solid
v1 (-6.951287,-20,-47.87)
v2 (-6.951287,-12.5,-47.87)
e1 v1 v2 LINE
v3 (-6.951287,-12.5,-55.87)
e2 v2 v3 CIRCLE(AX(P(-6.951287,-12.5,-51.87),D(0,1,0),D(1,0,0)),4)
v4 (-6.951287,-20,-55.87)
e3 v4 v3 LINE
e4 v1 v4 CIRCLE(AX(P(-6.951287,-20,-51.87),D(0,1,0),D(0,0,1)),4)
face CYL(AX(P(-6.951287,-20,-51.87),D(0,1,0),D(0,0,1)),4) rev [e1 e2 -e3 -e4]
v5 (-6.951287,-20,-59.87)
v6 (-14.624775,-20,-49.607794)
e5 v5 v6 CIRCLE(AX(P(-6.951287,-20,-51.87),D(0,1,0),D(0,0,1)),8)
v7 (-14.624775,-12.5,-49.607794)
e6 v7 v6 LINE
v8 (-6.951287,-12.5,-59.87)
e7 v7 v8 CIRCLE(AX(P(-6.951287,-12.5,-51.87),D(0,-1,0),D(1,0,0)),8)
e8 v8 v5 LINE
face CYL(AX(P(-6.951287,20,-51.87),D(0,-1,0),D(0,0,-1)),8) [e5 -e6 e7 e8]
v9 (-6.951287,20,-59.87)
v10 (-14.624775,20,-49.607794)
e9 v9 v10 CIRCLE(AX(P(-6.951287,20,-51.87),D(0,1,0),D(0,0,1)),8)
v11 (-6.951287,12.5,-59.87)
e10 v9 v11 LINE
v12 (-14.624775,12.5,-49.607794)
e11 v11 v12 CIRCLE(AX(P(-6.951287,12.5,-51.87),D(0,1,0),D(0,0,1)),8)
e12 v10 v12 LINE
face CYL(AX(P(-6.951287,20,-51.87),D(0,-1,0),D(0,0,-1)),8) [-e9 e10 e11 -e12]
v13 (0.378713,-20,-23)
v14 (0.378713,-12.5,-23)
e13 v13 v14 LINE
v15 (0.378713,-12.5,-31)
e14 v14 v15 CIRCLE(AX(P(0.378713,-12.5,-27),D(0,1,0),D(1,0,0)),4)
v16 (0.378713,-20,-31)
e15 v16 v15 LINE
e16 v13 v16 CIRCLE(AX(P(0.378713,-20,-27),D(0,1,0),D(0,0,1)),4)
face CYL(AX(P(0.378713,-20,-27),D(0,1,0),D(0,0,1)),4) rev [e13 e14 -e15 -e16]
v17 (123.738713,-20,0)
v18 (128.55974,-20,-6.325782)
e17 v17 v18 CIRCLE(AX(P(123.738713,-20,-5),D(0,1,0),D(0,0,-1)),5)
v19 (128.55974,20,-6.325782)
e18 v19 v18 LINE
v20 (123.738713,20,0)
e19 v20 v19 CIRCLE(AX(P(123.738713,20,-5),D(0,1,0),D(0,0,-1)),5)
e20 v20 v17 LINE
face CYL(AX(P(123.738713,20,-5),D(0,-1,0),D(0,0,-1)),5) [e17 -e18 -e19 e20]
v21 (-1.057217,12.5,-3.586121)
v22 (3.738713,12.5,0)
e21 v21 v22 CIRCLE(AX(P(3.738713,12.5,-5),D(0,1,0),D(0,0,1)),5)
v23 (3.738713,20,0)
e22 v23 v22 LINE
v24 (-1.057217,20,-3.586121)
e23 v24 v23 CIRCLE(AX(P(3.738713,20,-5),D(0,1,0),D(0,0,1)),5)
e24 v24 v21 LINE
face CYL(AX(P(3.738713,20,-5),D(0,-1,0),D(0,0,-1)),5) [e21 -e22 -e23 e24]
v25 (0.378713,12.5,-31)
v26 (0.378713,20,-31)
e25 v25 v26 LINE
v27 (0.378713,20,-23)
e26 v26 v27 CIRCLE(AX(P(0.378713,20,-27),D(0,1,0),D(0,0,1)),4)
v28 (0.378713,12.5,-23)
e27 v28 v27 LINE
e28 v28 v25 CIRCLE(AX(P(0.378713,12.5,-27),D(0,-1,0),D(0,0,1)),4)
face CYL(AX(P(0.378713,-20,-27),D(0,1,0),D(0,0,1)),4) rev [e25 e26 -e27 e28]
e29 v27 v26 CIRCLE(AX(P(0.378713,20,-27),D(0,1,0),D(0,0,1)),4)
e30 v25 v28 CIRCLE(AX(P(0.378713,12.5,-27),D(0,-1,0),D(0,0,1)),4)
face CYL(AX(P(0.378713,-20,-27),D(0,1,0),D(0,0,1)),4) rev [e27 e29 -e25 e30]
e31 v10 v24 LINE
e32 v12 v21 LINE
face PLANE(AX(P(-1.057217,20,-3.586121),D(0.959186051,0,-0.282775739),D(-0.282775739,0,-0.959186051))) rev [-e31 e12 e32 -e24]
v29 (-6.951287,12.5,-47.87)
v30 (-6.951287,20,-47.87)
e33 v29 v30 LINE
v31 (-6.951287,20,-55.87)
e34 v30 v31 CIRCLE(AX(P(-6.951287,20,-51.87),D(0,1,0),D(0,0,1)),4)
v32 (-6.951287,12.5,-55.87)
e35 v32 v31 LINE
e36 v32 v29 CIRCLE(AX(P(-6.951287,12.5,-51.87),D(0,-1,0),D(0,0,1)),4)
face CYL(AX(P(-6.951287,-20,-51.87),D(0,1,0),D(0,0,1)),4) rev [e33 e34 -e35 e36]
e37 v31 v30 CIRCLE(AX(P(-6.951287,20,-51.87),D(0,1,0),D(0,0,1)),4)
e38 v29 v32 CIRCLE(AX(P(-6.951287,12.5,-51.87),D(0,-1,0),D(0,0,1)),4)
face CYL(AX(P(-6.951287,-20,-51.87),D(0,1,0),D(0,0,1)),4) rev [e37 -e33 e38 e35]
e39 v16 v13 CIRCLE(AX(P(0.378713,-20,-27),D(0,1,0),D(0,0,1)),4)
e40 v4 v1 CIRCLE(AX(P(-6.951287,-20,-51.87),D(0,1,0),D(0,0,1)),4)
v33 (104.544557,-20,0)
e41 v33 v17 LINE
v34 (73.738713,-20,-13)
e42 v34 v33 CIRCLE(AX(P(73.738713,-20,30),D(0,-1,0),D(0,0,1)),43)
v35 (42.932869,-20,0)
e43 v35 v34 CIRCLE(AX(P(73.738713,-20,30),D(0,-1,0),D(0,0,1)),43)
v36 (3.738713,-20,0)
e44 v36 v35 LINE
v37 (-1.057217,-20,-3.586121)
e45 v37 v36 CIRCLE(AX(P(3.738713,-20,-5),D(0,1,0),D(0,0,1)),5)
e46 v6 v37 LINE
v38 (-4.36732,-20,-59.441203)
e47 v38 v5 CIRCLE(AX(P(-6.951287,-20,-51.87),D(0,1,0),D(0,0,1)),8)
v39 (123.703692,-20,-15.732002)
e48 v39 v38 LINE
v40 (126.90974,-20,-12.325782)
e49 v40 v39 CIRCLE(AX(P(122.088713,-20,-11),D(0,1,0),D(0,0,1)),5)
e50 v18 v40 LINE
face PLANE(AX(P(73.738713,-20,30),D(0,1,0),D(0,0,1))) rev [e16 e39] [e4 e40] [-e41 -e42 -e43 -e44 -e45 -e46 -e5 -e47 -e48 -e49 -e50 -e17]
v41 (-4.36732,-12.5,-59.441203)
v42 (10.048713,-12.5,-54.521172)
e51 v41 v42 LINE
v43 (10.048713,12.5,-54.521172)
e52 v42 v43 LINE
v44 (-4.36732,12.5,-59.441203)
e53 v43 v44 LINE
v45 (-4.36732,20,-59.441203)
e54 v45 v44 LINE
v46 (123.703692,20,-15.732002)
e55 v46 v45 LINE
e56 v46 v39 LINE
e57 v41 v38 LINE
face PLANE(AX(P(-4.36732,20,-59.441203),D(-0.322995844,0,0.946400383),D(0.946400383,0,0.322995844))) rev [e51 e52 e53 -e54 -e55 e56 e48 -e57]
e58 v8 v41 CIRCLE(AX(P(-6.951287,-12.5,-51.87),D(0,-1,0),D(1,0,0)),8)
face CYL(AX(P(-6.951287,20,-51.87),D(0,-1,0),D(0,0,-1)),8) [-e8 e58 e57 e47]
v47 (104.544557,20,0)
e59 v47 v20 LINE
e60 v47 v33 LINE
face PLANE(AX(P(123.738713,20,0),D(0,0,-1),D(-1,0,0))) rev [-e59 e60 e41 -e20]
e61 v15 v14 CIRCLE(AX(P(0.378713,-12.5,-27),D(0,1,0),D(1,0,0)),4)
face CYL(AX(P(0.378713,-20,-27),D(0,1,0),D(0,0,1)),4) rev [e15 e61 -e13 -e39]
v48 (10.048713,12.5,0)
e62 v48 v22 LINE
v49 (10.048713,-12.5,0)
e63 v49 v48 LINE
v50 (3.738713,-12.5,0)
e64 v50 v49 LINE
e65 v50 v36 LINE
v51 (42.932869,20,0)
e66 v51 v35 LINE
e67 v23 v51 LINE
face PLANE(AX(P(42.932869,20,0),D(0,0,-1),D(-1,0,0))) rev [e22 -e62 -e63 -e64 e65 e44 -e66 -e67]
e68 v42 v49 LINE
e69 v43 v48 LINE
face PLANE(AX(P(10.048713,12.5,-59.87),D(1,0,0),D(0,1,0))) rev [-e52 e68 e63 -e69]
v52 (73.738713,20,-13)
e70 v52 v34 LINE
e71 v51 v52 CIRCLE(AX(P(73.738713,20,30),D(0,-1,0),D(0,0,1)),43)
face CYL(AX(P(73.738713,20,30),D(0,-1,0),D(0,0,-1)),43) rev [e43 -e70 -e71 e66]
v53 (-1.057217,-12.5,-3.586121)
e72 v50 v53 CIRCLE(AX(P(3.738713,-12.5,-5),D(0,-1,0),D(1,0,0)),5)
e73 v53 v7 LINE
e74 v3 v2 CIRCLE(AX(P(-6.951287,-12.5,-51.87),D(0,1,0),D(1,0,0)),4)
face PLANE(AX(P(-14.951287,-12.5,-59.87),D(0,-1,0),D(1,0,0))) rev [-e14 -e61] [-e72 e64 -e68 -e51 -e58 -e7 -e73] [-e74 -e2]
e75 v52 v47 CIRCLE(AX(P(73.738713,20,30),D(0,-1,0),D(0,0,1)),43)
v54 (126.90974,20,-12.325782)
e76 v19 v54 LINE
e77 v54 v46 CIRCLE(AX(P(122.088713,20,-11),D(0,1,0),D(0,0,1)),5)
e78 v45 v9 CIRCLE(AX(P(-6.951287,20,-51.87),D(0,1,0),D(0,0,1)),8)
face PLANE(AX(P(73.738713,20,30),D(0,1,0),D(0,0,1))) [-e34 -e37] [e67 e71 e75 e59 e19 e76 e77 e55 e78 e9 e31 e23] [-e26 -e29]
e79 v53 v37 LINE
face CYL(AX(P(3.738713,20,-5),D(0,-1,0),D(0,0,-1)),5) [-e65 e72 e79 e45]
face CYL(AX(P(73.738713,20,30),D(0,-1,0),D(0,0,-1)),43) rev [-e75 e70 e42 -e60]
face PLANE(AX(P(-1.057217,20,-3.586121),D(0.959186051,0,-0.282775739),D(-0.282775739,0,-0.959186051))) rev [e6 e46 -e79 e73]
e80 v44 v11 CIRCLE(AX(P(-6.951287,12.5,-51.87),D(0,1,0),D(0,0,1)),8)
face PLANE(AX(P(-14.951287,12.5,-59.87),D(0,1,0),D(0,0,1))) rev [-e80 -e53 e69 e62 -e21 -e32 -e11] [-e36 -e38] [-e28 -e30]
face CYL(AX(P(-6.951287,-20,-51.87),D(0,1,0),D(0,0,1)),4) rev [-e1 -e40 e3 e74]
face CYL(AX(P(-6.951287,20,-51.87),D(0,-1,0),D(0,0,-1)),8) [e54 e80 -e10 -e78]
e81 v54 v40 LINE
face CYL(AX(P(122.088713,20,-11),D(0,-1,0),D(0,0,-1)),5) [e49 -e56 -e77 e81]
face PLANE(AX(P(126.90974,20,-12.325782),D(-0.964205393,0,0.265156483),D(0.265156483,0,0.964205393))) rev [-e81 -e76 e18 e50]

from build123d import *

# Parameters (mm, degrees)
BRACKET_BODY_DEPTH        = 20
MOUNTING_HOLES_SKETCH_R   = 4
MOUNTING_HOLES_2X_8_DEPTH = 20
END_SLOT_SKETCH_W         = 25
END_SLOT_SKETCH_H         = 25
END_SLOT_25_WIDE_DEPTH    = 144.380867308


with BuildPart() as part:
    # Bracket Profile Sketch → Bracket Body (new, symmetric)
    with BuildSketch(Plane(origin=(0, 0, 0), x_dir=(1, 0, 0), z_dir=(0, 1, 0))):
        with BuildLine():
            Line((-1.057217315, 3.586121305), (-14.62477547, 49.607794087))
            ThreePointArc((-14.62477547, 49.607794087), (-12.487512371, 57.644964007), (-4.367320309, 59.441203064))
            Line((-4.367320309, 59.441203064), (123.70369216, 15.732001915))
            ThreePointArc((123.70369216, 15.732001915), (125.729609358, 14.426933511), (126.909739906, 12.325782415))
            Line((126.909739906, 12.325782415), (128.559739906, 6.325782415))
            ThreePointArc((128.559739906, 6.325782415), (127.715452315, 1.969233766), (123.738712942, 0))
            Line((123.738712942, 0), (104.544556544, 0))
            ThreePointArc((104.544556544, 0), (73.738712942, 13), (42.932869341, 0))
            Line((42.932869341, 0), (3.738712942, 0))
            ThreePointArc((3.738712942, 0), (0.744501316, 0.995665256), (-1.057217315, 3.586121305))
        make_face()
    extrude(amount=BRACKET_BODY_DEPTH, both=True)

    # Mounting Holes Sketch → Mounting Holes 2xØ8 (cut, symmetric)
    with BuildSketch(Plane(origin=(0, 0, 0), x_dir=(1, 0, 0), z_dir=(0, 1, 0))):
        with Locations(Location((-6.951287058, 51.87, 0), (0, 0, 270))):
            Circle(MOUNTING_HOLES_SKETCH_R)
        with Locations(Location((0.378712942, 27, 0), (0, 0, 270))):
            Circle(MOUNTING_HOLES_SKETCH_R)
    extrude(amount=MOUNTING_HOLES_2X_8_DEPTH, both=True, mode=Mode.SUBTRACT)

    # End Slot Sketch → End Slot 25 Wide (cut, through all)
    with BuildSketch(Plane.XY):
        with Locations((-2.451287058, 0)):
            Rectangle(END_SLOT_SKETCH_W, END_SLOT_SKETCH_H)
    extrude(amount=-END_SLOT_25_WIDE_DEPTH, mode=Mode.SUBTRACT)


solid = part.part
